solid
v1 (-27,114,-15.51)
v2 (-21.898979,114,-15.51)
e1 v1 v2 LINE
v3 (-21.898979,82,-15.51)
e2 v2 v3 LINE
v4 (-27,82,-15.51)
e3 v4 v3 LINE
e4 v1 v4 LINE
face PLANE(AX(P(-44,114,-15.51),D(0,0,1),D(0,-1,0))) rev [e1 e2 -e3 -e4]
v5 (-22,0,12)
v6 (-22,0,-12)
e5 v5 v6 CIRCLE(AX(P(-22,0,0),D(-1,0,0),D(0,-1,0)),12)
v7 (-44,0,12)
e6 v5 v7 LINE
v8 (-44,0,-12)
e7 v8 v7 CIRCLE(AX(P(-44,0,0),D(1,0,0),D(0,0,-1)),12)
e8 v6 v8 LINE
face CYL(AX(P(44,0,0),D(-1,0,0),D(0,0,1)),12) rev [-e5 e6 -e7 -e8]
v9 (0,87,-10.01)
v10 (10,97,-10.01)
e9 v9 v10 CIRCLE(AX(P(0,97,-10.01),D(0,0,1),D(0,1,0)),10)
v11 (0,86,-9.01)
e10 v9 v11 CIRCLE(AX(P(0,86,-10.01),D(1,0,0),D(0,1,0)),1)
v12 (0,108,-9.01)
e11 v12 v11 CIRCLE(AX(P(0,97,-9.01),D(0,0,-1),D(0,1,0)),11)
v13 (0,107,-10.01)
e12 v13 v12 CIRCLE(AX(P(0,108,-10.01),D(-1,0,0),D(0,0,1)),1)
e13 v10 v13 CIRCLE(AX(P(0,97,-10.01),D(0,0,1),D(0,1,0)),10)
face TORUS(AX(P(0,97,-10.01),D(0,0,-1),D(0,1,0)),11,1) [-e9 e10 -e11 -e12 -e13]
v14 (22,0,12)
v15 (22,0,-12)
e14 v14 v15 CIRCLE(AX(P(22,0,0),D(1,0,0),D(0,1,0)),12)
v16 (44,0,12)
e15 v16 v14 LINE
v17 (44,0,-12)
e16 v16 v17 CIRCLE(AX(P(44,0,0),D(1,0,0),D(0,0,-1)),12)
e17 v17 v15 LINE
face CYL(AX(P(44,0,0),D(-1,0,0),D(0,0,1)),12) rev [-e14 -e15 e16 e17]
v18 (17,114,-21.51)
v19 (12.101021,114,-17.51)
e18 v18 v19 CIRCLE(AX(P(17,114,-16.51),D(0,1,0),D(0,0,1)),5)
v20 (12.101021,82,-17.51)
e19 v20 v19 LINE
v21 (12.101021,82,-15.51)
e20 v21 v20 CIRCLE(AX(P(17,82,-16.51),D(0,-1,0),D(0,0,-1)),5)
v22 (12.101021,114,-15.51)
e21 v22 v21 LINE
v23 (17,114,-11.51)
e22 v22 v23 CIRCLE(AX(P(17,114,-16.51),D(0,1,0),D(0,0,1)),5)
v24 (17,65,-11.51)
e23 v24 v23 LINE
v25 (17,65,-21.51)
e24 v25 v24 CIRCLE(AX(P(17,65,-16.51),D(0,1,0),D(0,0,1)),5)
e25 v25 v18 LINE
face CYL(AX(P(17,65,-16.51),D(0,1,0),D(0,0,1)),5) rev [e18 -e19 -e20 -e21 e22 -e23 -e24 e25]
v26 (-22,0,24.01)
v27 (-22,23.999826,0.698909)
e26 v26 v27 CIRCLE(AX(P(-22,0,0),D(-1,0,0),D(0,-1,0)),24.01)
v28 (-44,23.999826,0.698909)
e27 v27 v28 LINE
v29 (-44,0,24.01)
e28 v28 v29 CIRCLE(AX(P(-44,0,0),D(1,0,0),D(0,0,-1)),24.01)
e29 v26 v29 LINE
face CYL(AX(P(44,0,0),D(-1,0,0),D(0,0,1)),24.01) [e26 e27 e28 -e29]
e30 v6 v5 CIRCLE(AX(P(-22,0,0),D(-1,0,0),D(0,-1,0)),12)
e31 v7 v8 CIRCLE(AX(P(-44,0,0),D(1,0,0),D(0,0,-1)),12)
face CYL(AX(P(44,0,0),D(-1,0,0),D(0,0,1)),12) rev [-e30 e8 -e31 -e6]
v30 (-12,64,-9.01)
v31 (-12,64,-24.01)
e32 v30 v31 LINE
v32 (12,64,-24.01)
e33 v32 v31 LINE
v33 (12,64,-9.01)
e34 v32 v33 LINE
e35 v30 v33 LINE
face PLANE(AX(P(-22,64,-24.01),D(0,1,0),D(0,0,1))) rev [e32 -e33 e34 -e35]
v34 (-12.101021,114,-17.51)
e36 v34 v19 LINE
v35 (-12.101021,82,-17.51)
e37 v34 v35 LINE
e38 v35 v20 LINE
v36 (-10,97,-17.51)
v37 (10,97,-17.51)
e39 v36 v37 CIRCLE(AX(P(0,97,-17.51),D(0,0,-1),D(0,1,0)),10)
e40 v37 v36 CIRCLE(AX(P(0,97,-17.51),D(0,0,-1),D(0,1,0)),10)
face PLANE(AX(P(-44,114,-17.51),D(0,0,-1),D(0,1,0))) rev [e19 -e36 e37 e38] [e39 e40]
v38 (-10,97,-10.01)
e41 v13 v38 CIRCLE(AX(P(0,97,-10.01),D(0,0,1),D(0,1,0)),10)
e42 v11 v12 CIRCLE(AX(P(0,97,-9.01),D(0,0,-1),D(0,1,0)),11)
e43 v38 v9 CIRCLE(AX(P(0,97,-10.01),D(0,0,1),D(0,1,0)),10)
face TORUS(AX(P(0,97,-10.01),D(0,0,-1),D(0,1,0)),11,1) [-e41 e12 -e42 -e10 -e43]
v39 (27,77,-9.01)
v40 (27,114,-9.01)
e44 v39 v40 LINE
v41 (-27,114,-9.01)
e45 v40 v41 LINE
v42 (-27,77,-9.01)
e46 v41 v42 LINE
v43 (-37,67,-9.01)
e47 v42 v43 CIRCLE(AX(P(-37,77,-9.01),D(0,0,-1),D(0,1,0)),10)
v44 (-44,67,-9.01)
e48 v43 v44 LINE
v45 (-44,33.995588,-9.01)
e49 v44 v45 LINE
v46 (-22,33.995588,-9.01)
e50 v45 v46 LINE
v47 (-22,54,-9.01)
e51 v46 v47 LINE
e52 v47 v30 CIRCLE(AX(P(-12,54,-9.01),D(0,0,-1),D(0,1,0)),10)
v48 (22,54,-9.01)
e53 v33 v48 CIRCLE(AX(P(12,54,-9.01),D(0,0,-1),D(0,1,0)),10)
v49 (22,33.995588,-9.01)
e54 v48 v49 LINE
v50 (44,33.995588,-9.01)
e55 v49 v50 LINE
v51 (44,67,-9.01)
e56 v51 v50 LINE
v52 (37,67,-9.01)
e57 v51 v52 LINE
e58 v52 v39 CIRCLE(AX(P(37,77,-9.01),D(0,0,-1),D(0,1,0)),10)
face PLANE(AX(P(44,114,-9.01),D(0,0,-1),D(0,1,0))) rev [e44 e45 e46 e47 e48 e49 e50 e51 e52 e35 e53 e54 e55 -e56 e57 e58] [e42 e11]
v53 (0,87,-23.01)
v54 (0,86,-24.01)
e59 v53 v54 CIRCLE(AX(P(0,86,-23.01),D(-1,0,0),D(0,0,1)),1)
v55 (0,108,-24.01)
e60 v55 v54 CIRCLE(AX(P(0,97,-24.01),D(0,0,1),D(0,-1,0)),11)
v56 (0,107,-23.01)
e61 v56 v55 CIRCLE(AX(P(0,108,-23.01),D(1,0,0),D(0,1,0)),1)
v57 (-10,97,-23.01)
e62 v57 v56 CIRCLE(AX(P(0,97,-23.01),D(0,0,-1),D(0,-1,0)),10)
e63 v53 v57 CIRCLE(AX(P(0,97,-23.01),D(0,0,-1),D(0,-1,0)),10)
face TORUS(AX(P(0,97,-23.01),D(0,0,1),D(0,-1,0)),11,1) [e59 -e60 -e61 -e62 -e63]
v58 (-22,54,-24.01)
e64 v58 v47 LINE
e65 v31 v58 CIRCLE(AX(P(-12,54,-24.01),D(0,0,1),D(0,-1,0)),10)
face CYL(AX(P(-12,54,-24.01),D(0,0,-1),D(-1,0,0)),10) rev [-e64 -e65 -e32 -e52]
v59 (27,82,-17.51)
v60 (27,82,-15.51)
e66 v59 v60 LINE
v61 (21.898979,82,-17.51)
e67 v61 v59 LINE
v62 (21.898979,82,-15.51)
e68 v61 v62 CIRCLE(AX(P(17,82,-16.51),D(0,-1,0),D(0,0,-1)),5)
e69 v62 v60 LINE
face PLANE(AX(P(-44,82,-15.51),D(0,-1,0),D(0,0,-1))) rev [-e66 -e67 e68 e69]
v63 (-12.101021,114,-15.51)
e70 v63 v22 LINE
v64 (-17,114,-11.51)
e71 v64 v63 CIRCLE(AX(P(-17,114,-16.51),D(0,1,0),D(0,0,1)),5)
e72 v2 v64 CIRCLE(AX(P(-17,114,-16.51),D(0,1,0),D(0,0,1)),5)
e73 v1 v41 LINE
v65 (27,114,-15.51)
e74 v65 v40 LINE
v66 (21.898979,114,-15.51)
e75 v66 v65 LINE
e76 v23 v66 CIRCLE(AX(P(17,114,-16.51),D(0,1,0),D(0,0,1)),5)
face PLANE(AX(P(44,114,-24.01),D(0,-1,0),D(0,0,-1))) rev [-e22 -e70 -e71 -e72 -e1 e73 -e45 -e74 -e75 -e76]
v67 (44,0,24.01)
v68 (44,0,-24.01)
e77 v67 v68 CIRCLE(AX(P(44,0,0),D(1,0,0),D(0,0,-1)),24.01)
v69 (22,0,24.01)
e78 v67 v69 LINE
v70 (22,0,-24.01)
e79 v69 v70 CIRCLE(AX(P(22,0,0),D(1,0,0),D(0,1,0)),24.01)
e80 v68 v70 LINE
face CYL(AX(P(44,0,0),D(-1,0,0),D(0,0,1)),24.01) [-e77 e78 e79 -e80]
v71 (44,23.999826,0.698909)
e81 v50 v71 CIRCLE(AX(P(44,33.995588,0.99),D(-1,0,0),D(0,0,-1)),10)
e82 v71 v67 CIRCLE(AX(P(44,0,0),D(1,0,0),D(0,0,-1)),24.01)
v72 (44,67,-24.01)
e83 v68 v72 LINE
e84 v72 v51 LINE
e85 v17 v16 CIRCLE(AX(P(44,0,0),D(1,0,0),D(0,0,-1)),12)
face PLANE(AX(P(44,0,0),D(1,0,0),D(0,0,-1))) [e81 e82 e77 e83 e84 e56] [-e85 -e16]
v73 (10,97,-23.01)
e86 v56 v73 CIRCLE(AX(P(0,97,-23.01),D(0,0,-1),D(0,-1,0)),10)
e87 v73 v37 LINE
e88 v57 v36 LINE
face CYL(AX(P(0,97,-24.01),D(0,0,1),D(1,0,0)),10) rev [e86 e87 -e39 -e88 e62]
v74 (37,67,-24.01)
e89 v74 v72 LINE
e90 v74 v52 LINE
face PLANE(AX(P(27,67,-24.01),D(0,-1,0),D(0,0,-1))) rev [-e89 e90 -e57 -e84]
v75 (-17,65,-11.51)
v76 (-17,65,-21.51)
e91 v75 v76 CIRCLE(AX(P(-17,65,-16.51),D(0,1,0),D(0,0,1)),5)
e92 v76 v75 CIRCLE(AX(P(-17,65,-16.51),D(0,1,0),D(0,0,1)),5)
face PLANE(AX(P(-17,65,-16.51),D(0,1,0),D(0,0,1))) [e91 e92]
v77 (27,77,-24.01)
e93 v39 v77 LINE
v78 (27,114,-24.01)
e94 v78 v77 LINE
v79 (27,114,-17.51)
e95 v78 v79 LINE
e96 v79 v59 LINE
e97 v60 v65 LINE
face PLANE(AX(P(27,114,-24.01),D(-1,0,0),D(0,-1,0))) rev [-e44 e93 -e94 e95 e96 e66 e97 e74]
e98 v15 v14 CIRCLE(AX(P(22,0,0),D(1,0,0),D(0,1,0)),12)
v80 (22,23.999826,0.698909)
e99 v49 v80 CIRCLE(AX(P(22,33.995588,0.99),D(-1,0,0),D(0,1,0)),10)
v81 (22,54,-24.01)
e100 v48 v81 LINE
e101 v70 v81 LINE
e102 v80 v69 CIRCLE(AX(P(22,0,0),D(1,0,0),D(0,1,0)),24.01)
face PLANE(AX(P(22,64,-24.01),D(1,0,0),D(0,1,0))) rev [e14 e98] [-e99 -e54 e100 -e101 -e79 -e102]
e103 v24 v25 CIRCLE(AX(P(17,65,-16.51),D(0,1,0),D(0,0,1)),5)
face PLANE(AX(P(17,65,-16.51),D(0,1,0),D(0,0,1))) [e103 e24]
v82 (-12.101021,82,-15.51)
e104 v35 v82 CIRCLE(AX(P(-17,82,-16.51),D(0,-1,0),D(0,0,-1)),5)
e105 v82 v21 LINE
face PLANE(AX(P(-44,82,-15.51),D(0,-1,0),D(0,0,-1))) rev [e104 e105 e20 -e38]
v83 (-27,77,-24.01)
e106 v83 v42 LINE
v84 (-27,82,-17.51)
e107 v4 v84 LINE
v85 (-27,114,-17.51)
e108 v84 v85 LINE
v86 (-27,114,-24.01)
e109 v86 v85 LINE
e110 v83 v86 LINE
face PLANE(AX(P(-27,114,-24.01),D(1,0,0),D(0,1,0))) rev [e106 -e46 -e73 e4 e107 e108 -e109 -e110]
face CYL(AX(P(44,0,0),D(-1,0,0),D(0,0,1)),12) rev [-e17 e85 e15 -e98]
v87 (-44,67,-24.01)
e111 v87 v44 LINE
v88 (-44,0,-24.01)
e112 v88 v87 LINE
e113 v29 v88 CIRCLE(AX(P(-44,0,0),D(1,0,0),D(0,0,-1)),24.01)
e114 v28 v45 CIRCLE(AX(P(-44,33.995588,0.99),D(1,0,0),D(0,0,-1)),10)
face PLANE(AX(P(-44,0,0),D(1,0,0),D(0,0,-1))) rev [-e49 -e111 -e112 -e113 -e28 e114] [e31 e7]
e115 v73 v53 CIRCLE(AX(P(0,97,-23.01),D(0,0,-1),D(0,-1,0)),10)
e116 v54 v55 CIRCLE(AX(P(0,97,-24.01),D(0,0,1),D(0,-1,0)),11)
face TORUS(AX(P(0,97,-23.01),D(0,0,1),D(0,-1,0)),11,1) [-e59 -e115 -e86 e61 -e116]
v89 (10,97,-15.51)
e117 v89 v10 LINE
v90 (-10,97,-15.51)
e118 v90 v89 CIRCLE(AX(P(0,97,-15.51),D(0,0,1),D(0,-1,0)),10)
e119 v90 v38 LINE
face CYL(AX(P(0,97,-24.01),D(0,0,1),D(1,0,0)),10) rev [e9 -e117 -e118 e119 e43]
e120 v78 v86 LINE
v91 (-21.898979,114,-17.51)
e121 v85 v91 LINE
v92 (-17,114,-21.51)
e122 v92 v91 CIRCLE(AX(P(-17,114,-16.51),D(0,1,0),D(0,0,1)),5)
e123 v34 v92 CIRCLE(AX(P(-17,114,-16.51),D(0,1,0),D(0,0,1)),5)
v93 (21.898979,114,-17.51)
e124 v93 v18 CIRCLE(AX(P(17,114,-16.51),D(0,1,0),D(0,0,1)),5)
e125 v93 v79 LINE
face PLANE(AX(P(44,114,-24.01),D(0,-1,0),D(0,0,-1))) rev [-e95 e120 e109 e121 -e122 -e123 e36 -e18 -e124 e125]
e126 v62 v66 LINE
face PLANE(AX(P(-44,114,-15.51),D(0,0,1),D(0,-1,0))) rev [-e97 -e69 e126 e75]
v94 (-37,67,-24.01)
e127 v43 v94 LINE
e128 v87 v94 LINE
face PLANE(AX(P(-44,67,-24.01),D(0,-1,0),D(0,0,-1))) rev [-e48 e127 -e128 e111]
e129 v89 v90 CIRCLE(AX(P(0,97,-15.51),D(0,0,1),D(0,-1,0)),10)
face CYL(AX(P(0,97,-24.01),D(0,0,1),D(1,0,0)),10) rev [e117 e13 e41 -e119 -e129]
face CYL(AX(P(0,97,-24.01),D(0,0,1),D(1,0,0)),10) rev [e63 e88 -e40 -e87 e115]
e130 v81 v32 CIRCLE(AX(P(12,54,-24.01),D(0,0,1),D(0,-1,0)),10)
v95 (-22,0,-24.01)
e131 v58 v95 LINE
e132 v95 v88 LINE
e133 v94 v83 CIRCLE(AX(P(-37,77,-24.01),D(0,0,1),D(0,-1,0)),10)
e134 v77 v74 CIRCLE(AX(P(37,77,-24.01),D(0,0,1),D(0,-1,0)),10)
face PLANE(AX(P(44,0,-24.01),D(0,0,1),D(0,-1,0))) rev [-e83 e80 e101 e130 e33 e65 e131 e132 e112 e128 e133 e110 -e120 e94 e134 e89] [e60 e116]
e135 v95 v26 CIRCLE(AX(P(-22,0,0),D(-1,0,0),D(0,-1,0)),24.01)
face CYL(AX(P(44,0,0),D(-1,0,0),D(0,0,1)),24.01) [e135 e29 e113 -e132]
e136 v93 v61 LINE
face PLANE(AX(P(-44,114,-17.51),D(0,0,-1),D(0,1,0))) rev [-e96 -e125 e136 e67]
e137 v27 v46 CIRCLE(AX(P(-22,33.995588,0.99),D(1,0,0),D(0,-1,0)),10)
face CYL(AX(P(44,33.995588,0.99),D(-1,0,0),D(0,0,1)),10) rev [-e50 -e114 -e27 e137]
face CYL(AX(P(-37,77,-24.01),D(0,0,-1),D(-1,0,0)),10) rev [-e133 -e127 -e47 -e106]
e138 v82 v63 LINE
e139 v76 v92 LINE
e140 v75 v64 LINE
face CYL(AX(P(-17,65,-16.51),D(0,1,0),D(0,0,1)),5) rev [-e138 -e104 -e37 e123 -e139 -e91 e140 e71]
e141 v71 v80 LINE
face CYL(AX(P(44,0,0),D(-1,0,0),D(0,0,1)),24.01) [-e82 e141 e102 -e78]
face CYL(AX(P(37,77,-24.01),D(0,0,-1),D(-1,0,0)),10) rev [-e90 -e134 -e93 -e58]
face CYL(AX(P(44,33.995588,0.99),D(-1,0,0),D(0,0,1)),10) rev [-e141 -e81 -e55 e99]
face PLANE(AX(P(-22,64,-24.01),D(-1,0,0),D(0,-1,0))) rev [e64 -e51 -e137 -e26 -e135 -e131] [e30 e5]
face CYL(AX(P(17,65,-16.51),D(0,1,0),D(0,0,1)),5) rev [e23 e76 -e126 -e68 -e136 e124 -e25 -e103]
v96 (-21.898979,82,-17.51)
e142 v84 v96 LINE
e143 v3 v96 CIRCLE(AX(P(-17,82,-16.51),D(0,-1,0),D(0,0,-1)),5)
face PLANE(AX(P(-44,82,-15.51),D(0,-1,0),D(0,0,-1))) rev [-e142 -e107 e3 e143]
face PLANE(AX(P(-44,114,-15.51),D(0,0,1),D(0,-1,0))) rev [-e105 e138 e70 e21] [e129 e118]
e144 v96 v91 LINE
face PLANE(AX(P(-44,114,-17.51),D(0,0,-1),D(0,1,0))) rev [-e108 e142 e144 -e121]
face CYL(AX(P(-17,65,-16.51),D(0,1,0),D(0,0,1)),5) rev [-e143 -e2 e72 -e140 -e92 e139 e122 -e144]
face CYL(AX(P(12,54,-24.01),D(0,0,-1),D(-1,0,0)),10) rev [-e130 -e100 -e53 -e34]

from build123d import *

# Parameters (mm, degrees)
LUG_BARREL_SKETCH_R           = 24.01
LUG_BARREL_SKETCH_R_2         = 12
ROLLER_LUG_BARREL_DEPTH       = 44
MOUNTING_PLATE_DEPTH          = 44
PLATE_TO_BARREL_FILLET_R10_R  = 10
PLATE_SHOULDER_CUT_DEPTH      = 125.533048224
PLATE_SHOULDER_CUT_DEPTH_BACK = 125.533048224
PLATE_SHOULDER_CUT_SKETCH_W   = 44
PLATE_SHOULDER_CUT_SKETCH_H   = 88.01
LUG_GAP_CUT_DEPTH             = 125.533048224
LUG_GAP_CUT_DEPTH_BACK        = 125.533048224
LUG_GAP_SKETCH_W              = 17
LUG_GAP_SKETCH_H              = 47
LUG_GAP_FILLET_R10_R          = 10
CLAMP_SLIT_2MM_DEPTH          = 125.533048224
CLAMP_SLIT_2MM_DEPTH_BACK     = 125.533048224
CLAMP_SLIT_SKETCH_W           = 2
CLAMP_SLIT_SKETCH_H           = 32
PLATE_HOLE_20_DEPTH           = 127.579304786
PLATE_HOLE_20_DEPTH_BACK      = 127.579304786
PLATE_HOLE_SKETCH_R           = 10
PLATE_HOLE_EDGE_FILLET_R1_R   = 1
CLAMP_SCREW_SKETCH_R          = 5
CLAMP_SCREW_CUT_DEPTH         = 49


with BuildPart() as part:
    # Lug Barrel Sketch → Roller Lug Barrel (new, symmetric)
    with BuildSketch(Plane(origin=(0, 0, 0), x_dir=(0, 0, -1), z_dir=(1, 0, 0))):
        Circle(LUG_BARREL_SKETCH_R)
        Circle(LUG_BARREL_SKETCH_R_2, mode=Mode.SUBTRACT)
    extrude(amount=ROLLER_LUG_BARREL_DEPTH, both=True)

    # Mounting Plate Sketch → Mounting Plate (add, symmetric)
    with BuildSketch(Plane(origin=(0, 0, 0), x_dir=(0, 0, -1), z_dir=(1, 0, 0))):
        with BuildLine():
            Line((24.01, 0), (24.01, 114))
            Line((24.01, 114), (9.01, 114))
            Line((9.01, 114), (9.01, 22.255336439))
            ThreePointArc((9.01, 22.255336439), (19.909924661, 13.419202659), (24.01, 0))
        make_face()
    extrude(amount=MOUNTING_PLATE_DEPTH, both=True)

    # Plate to Barrel Fillet R10
    plate_to_barrel_fillet_r10_edges = [part.edges().sort_by_distance(p)[0] for p in [
        (0, 22.255336439, -9.01),
    ]]
    fillet(plate_to_barrel_fillet_r10_edges, radius=PLATE_TO_BARREL_FILLET_R10_R)

    # Plate Shoulder Cut Sketch → Plate Shoulder Cut (cut, two sides: drawn at the far end of the back side and taken through both)
    with BuildSketch(Plane.XY.offset(-PLATE_SHOULDER_CUT_DEPTH_BACK)):
        with Locations((0, 19.995)):
            Rectangle(PLATE_SHOULDER_CUT_SKETCH_W, PLATE_SHOULDER_CUT_SKETCH_H)
    extrude(amount=PLATE_SHOULDER_CUT_DEPTH + PLATE_SHOULDER_CUT_DEPTH_BACK, mode=Mode.SUBTRACT)

    # Lug Gap Sketch → Lug Gap Cut (cut, two sides: drawn at the far end of the back side and taken through both)
    with BuildSketch(Plane.XY.offset(-LUG_GAP_CUT_DEPTH_BACK)):
        with Locations((-35.5, 90.5)):
            Rectangle(LUG_GAP_SKETCH_W, LUG_GAP_SKETCH_H)
        with Locations((35.5, 90.5)):
            Rectangle(LUG_GAP_SKETCH_W, LUG_GAP_SKETCH_H)
    extrude(amount=LUG_GAP_CUT_DEPTH + LUG_GAP_CUT_DEPTH_BACK, mode=Mode.SUBTRACT)

    # Lug Gap Fillet R10
    lug_gap_fillet_r10_edges = [part.edges().sort_by_distance(p)[0] for p in [
        (-22, 64, -16.51),
        (22, 64, -16.51),
        (-27, 67, -16.51),
        (27, 67, -16.51),
    ]]
    fillet(lug_gap_fillet_r10_edges, radius=LUG_GAP_FILLET_R10_R)

    # Clamp Slit Sketch → Clamp Slit 2mm (cut, two sides: drawn at the far end of the back side and taken through both)
    with BuildSketch(Plane(origin=(0, 0, 0), x_dir=(0, 0, -1), z_dir=(1, 0, 0)).offset(-CLAMP_SLIT_2MM_DEPTH_BACK)):
        with Locations((16.51, 98)):
            Rectangle(CLAMP_SLIT_SKETCH_W, CLAMP_SLIT_SKETCH_H)
    extrude(amount=CLAMP_SLIT_2MM_DEPTH + CLAMP_SLIT_2MM_DEPTH_BACK, mode=Mode.SUBTRACT)

    # Plate Hole Sketch → Plate Hole Ø20 (cut, two sides: drawn at the far end of the back side and taken through both)
    with BuildSketch(Plane.XY.offset(-9.01).offset(-PLATE_HOLE_20_DEPTH_BACK)):
        with Locations((0, 97)):
            Circle(PLATE_HOLE_SKETCH_R)
    extrude(amount=PLATE_HOLE_20_DEPTH + PLATE_HOLE_20_DEPTH_BACK, mode=Mode.SUBTRACT)

    # Plate Hole Edge Fillet R1
    plate_hole_edge_fillet_r1_edges = [part.edges().sort_by_distance(p)[0] for p in [
        (-10, 97, -9.01),
        (-10, 97, -24.01),
    ]]
    fillet(plate_hole_edge_fillet_r1_edges, radius=PLATE_HOLE_EDGE_FILLET_R1_R)

    # Clamp Screw Sketch → Clamp Screw Cut (cut)
    with BuildSketch(Plane(origin=(0, 114, 0), x_dir=(1, 0, 0), z_dir=(0, 1, 0))):
        with Locations(Location((-17, 16.51, 0), (0, 0, 270))):
            Circle(CLAMP_SCREW_SKETCH_R)
        with Locations(Location((17, 16.51, 0), (0, 0, 270))):
            Circle(CLAMP_SCREW_SKETCH_R)
    extrude(amount=-CLAMP_SCREW_CUT_DEPTH, mode=Mode.SUBTRACT)


solid = part.part
